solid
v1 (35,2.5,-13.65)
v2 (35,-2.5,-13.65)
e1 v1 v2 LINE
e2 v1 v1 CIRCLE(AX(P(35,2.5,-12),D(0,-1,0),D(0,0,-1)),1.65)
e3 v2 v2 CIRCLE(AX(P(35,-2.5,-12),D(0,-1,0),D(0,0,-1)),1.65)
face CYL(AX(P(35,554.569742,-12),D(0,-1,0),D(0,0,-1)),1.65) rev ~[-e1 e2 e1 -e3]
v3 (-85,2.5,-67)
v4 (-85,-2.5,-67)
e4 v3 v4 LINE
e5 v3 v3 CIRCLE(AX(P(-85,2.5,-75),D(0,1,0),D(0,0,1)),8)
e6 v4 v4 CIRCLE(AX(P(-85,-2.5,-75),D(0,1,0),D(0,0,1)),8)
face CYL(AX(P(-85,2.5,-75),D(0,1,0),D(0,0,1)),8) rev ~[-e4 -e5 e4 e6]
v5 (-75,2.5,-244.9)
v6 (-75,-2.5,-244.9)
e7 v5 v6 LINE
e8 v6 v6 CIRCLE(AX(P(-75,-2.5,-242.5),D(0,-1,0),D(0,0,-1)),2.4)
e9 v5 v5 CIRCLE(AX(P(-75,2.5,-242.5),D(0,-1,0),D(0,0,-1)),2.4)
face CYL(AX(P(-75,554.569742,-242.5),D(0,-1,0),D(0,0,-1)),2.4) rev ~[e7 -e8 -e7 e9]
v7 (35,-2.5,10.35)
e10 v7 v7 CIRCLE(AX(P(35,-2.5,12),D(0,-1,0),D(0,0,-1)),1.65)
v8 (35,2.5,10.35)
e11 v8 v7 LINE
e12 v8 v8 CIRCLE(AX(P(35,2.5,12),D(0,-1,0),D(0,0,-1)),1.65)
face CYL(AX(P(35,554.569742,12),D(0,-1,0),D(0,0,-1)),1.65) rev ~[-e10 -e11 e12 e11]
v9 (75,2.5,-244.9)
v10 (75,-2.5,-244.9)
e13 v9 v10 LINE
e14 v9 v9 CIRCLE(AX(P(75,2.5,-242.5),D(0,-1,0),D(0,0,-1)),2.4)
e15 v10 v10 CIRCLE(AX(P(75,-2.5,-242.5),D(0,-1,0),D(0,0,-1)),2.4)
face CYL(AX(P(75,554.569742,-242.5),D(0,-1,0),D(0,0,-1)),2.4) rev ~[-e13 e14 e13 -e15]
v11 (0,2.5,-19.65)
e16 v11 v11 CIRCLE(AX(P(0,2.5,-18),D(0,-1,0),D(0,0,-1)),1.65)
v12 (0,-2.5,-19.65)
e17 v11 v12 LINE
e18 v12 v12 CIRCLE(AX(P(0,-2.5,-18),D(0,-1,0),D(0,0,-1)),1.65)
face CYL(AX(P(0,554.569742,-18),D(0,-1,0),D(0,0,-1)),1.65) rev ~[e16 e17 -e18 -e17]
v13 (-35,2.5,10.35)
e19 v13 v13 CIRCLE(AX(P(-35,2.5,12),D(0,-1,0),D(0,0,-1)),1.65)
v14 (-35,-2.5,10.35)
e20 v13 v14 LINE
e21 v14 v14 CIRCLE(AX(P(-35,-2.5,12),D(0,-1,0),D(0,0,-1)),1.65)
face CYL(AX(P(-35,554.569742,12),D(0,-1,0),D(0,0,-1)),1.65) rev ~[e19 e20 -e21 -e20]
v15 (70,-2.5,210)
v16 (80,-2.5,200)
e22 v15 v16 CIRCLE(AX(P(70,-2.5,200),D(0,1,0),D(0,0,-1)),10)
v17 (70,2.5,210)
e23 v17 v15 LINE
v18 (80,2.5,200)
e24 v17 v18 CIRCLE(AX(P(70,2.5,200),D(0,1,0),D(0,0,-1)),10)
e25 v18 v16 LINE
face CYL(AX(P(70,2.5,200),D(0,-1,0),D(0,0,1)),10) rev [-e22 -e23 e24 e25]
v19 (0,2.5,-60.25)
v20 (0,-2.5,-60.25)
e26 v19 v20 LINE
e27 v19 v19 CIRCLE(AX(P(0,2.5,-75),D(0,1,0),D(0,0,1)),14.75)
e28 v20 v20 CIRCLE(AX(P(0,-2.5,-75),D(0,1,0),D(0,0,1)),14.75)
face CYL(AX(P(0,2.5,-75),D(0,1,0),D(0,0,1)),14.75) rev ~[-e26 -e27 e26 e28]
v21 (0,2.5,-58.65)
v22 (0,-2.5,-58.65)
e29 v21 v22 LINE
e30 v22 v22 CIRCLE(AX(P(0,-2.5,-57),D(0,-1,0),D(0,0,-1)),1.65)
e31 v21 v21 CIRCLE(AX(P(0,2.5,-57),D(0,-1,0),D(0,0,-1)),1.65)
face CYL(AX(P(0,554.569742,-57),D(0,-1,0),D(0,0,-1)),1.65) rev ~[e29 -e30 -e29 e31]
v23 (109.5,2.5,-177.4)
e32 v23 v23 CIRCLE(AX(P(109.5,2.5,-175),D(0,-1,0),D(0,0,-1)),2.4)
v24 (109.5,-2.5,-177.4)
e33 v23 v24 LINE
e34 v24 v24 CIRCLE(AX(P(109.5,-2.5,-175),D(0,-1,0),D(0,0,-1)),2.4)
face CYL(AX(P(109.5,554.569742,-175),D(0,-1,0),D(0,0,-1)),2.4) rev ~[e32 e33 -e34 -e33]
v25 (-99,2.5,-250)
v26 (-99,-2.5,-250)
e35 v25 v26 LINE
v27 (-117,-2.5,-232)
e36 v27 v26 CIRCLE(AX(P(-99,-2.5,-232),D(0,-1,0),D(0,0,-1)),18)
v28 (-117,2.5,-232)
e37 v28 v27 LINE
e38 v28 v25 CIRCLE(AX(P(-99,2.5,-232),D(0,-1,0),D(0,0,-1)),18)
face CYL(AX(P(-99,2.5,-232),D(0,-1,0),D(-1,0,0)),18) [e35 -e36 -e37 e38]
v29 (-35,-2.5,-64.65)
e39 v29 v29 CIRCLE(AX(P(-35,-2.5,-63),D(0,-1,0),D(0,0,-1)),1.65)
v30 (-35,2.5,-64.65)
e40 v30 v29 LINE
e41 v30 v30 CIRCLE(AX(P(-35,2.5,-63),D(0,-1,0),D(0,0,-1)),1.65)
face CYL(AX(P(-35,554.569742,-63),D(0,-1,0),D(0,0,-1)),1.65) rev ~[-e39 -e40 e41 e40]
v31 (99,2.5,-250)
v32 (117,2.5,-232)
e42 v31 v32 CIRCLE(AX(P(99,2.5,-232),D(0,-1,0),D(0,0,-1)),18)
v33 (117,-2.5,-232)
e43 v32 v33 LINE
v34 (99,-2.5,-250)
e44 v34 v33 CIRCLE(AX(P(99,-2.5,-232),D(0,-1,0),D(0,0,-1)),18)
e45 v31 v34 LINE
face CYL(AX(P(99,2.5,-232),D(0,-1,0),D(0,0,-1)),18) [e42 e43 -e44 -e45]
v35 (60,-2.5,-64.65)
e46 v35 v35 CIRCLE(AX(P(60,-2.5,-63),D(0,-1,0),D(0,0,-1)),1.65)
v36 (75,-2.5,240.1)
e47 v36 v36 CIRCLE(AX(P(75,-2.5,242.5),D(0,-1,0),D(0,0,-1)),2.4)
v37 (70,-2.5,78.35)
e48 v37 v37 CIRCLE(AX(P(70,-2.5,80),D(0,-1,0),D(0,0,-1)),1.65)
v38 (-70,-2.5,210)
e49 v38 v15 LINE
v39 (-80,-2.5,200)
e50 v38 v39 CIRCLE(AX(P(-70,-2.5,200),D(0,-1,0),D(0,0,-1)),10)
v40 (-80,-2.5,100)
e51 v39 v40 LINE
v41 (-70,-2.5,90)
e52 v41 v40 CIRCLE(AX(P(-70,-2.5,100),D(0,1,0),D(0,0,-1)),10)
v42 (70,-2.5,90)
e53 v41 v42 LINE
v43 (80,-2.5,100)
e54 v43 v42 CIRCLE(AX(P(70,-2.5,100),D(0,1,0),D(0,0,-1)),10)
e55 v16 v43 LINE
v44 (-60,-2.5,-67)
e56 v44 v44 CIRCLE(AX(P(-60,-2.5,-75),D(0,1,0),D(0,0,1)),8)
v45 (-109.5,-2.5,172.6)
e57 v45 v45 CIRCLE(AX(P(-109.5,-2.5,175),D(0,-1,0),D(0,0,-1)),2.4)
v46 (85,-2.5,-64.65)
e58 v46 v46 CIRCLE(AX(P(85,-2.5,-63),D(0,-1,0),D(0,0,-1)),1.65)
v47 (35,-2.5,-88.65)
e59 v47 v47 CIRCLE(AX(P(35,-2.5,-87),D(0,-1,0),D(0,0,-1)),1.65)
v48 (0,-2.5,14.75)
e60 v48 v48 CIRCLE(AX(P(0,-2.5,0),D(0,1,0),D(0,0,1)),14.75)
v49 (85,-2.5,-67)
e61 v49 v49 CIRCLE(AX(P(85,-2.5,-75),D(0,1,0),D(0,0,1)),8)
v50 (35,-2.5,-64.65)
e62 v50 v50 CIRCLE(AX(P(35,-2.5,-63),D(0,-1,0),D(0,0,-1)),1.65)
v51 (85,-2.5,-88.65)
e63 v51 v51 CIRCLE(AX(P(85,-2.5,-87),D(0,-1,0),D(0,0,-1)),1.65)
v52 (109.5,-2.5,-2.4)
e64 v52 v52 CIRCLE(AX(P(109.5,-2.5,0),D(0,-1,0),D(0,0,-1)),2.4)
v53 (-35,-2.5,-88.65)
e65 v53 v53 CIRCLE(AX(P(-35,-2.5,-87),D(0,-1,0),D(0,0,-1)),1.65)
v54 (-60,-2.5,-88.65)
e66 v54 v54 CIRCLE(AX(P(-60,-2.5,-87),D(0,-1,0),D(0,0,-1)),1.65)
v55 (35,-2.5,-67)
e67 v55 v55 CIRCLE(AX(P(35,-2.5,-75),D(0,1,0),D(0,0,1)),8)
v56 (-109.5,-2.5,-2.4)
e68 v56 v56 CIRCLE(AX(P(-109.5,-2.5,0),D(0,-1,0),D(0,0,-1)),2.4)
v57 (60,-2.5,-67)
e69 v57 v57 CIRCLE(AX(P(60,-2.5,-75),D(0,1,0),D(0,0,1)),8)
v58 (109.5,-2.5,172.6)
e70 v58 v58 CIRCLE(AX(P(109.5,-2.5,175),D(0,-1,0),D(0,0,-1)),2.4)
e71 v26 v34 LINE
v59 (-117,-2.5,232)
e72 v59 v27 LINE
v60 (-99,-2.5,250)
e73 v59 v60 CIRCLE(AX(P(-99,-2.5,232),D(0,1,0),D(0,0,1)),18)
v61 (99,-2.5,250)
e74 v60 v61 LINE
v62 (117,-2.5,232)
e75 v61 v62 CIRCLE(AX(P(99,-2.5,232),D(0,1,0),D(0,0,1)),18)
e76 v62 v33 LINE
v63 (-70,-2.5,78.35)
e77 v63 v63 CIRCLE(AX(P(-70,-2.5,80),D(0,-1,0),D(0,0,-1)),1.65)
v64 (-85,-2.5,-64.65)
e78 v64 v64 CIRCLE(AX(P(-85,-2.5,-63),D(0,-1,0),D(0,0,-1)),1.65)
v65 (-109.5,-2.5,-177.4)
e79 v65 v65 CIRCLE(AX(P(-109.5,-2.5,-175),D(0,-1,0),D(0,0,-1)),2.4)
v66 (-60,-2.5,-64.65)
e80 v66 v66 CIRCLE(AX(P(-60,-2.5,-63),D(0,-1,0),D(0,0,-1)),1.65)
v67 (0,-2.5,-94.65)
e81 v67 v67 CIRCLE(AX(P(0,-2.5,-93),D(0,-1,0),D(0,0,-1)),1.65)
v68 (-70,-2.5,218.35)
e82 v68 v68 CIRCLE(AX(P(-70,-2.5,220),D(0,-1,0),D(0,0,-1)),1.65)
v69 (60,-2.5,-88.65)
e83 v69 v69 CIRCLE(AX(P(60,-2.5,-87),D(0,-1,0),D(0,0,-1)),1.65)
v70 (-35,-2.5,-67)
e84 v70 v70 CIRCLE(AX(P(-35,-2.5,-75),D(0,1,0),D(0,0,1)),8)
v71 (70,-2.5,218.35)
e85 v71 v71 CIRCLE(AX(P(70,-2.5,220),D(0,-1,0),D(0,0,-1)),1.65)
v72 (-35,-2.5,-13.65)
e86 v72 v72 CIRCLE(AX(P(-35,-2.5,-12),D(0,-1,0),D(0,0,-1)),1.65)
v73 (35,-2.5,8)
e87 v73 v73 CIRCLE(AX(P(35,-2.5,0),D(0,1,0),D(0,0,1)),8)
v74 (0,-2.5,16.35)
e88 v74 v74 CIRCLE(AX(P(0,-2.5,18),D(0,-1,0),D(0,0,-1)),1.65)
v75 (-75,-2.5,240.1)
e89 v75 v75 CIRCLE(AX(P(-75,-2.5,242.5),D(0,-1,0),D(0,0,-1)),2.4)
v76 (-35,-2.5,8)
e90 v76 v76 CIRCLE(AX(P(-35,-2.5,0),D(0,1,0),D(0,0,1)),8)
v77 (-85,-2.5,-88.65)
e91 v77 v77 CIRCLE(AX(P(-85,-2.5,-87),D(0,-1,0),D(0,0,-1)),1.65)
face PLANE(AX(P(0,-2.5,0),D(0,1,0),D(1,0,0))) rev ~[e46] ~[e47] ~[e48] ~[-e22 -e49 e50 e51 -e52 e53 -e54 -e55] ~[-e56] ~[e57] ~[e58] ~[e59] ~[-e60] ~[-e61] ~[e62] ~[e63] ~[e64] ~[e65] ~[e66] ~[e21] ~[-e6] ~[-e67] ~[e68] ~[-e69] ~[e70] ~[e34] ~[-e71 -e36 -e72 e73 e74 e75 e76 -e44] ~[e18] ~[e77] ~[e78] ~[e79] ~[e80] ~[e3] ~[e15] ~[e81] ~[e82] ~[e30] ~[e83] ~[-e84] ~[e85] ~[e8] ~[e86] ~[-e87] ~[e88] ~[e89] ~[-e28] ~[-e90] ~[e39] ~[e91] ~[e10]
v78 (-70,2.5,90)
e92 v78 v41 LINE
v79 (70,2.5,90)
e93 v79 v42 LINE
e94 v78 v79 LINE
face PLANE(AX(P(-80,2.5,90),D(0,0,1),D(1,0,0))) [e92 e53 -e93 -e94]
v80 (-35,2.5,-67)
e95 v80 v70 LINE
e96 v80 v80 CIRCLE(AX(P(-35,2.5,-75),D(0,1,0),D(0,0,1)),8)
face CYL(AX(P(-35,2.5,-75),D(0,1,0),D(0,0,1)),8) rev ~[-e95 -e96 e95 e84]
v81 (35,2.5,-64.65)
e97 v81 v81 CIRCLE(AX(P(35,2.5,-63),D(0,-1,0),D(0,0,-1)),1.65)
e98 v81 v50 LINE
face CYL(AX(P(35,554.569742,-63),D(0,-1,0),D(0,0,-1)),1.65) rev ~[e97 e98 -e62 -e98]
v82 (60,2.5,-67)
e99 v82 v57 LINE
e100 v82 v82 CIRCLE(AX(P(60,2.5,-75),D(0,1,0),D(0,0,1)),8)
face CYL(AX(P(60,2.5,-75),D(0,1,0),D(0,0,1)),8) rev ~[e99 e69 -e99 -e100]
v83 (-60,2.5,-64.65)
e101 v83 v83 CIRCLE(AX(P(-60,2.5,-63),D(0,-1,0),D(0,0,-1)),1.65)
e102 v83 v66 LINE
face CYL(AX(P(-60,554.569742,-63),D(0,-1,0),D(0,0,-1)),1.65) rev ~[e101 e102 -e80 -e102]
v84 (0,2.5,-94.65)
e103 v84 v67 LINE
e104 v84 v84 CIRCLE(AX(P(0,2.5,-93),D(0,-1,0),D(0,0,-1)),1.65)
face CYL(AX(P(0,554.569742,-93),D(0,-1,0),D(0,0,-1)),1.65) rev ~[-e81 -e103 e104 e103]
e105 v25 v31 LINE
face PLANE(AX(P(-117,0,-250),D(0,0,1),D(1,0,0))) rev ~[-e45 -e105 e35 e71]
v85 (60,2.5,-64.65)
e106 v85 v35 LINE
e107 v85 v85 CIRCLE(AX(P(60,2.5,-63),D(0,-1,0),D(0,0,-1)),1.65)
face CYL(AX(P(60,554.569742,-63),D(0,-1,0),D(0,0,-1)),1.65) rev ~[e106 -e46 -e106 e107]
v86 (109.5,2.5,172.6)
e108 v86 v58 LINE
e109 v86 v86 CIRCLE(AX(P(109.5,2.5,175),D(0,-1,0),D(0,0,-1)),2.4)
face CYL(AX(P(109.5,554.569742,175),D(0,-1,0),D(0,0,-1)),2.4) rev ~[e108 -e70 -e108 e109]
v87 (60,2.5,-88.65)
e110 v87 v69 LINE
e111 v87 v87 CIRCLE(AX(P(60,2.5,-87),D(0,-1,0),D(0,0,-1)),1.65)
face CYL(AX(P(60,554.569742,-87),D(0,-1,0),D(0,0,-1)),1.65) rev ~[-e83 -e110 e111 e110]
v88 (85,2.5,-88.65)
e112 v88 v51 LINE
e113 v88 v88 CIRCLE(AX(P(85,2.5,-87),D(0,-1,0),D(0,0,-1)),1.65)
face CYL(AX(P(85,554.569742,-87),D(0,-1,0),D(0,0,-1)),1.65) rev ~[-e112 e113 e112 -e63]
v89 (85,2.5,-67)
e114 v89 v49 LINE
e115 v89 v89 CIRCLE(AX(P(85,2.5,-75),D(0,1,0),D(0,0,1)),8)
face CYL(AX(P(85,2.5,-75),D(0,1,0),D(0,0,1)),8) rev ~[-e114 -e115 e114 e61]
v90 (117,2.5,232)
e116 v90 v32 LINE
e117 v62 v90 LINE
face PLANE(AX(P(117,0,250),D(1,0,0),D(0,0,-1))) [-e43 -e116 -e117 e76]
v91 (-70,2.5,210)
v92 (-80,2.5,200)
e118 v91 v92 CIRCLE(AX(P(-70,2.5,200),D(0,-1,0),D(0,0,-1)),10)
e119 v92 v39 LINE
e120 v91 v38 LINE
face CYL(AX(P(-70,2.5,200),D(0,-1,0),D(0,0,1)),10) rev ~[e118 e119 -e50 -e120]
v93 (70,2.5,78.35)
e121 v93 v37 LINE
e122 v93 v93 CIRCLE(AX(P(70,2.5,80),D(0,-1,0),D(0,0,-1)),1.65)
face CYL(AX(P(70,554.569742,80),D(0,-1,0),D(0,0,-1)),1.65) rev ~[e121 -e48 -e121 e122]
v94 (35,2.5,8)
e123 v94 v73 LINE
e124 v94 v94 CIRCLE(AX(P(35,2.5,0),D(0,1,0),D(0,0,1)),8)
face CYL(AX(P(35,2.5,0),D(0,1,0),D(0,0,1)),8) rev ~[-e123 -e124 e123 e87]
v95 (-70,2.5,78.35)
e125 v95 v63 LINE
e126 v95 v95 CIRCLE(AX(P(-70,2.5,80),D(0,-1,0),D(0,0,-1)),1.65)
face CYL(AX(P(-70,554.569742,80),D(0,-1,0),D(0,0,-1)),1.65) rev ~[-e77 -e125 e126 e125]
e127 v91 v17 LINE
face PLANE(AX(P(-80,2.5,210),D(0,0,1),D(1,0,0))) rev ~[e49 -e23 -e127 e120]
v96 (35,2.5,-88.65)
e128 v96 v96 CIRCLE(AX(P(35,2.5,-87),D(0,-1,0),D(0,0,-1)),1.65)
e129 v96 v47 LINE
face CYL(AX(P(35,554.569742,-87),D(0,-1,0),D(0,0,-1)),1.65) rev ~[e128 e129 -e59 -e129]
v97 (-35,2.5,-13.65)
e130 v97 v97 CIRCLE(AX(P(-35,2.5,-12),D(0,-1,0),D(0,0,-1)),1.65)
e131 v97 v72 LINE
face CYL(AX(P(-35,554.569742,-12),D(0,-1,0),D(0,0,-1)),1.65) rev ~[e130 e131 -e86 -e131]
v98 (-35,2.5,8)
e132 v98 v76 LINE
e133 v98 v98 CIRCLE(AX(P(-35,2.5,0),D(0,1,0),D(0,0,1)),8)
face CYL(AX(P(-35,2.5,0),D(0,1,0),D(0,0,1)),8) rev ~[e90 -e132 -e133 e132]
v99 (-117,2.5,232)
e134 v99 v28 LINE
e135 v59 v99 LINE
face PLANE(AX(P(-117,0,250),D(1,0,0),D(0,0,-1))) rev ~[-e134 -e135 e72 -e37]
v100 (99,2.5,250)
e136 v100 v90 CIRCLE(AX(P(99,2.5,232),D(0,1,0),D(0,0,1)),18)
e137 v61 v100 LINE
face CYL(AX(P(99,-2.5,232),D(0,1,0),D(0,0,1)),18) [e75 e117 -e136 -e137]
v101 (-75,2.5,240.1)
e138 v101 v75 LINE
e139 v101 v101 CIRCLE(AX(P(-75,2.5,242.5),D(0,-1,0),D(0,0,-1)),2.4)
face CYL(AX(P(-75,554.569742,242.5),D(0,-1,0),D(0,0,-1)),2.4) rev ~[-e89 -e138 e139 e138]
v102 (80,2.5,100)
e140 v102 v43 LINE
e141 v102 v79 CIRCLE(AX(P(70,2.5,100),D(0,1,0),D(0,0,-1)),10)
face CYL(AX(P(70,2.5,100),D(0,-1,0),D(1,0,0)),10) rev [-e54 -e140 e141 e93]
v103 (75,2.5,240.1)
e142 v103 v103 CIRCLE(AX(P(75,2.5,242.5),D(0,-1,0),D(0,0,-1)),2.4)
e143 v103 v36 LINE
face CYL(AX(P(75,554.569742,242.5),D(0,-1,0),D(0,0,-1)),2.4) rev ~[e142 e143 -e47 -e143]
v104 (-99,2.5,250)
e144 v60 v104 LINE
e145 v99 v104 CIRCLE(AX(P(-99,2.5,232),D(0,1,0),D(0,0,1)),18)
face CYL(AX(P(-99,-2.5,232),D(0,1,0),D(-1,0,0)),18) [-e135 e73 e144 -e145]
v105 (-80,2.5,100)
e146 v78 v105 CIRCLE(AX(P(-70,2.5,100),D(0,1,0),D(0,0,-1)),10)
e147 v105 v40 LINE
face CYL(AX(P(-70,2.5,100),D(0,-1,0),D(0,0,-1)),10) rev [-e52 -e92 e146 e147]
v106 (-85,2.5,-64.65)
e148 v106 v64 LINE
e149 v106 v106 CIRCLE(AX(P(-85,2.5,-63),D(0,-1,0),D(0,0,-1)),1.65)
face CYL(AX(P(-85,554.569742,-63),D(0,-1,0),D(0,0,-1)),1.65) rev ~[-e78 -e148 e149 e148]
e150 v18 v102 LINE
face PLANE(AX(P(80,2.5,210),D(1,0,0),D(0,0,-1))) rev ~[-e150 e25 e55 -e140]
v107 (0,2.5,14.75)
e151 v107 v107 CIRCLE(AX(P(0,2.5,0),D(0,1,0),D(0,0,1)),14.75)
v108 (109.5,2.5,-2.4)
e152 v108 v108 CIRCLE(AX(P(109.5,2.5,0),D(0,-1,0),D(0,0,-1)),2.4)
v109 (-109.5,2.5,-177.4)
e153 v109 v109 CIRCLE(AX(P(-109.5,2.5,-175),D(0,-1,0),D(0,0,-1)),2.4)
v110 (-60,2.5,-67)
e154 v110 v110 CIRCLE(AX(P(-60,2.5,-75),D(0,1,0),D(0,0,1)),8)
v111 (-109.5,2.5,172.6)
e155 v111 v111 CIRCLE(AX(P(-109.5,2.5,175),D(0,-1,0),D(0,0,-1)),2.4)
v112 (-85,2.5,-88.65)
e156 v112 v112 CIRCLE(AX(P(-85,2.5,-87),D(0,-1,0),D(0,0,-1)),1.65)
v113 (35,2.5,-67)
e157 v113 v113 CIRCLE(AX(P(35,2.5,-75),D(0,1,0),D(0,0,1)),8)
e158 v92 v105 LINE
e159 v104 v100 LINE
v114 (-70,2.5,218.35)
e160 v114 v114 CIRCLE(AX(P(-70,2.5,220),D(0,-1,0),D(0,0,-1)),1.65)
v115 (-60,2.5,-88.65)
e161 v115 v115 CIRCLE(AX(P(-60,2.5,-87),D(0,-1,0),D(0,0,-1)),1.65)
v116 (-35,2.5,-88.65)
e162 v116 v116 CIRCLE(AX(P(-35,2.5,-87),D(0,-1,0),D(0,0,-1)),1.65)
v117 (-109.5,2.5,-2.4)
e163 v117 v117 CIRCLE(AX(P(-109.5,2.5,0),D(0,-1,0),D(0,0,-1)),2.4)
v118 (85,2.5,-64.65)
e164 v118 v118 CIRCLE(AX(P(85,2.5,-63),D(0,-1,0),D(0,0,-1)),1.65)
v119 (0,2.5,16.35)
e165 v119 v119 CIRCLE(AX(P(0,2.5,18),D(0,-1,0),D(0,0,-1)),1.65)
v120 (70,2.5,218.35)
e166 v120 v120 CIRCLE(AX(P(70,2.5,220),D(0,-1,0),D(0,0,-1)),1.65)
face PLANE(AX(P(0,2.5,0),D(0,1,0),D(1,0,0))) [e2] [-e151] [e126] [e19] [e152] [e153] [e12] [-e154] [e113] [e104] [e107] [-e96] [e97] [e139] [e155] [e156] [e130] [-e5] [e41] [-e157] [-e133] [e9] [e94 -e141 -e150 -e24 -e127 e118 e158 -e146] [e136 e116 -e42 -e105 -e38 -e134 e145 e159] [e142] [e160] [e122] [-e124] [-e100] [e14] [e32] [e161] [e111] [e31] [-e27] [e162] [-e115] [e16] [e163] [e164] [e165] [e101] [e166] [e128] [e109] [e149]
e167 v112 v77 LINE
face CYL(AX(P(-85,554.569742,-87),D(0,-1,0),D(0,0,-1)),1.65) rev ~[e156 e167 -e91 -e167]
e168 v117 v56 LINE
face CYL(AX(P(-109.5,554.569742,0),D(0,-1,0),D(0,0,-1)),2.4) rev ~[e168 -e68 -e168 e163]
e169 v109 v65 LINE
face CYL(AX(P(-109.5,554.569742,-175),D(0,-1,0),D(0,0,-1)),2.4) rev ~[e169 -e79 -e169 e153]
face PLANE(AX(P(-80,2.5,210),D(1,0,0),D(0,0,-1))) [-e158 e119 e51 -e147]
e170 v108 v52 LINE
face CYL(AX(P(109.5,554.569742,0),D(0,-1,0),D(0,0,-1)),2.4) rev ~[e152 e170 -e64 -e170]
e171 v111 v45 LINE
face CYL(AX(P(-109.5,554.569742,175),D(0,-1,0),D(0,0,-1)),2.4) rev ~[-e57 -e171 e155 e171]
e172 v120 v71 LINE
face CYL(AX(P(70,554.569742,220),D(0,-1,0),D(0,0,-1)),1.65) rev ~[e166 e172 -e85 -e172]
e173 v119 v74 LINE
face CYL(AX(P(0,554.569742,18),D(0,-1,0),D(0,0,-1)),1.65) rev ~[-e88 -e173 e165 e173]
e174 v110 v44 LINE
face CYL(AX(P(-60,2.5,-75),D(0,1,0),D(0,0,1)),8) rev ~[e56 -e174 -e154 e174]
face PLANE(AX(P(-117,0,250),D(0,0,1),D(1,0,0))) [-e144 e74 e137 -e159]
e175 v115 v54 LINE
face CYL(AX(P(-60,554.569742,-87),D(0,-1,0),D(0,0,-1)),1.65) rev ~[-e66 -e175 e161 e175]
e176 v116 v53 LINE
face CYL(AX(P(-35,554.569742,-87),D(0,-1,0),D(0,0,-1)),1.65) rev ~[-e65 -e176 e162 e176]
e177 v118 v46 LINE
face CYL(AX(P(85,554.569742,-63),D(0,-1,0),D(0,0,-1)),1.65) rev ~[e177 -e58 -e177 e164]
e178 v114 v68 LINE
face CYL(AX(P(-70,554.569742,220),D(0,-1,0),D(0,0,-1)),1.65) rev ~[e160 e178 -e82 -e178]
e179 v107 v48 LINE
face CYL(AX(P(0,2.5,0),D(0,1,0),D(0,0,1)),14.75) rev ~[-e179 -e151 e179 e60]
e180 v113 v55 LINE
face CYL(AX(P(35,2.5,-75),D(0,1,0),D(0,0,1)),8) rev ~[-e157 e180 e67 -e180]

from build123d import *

# Parameters (mm, degrees)
SKETCH1_W            = 234
SKETCH1_H            = 500
BOSS_EXTRUDE1_DEPTH  = 2.5
M4_CLEARANCE_HOLE1_D = 4.8
FILLET1_R            = 18
M4_TAPPED_HOLE7_D    = 3.3
SKETCH4_R            = 14.75
SKETCH4_R_2          = 8
CUT_EXTRUDE6_DEPTH   = 277.068831997
M4_TAPPED_HOLE3_D    = 3.3
SKETCH9_R            = 14.75
CUT_EXTRUDE3_DEPTH   = 277.068831997
M4_TAPPED_HOLE4_D    = 3.3
SKETCH12_W           = 160
SKETCH12_H           = 120
CUT_EXTRUDE4_DEPTH   = 277.068831997
FILLET2_R            = 10


with BuildPart() as part:
    # Sketch1 → Boss-Extrude1 (new, symmetric)
    with BuildSketch(Plane(origin=(0, 0, 0), x_dir=(1, 0, 0), z_dir=(0, 1, 0))):
        Rectangle(SKETCH1_W, SKETCH1_H)
    extrude(amount=BOSS_EXTRUDE1_DEPTH, both=True)

    # M4 Clearance Hole1 (through all)
    with Locations(Plane(origin=(-75, 2.5, -242.5), x_dir=(0, 0, 1), z_dir=(0, 1, 0))):
        with Locations((0, 0), (0, 150), (67.5, 184.5), (67.5, -34.5), (242.5, 184.5), (242.5, -34.5), (417.5, -34.5), (417.5, 184.5), (485, 0), (485, 150)):
            Hole(M4_CLEARANCE_HOLE1_D / 2)

    # Fillet1
    fillet1_edges = [part.edges().sort_by_distance(p)[0] for p in [
        (117, 0, 250),
        (-117, 0, 250),
        (-117, 0, -250),
        (117, 0, -250),
    ]]
    fillet(fillet1_edges, radius=FILLET1_R)

    # M4 Tapped Hole7 (through all)
    with Locations(Plane(origin=(-85, 2.5, -87), x_dir=(0, 0, 1), z_dir=(0, 1, 0))):
        with Locations((0, 0), (24, 0), (24, 25), (0, 25), (0, 50), (24, 50), (-6, 85), (30, 85), (0, 120), (24, 120), (0, 145), (24, 145), (0, 170), (24, 170), (75, 120), (99, 120), (75, 50), (99, 50)):
            Hole(M4_TAPPED_HOLE7_D / 2)

    # Sketch4 → Cut-Extrude6 (cut, through all)
    with BuildSketch(Plane(origin=(0, 2.5, 0), x_dir=(1, 0, 0), z_dir=(0, 1, 0))):
        with Locations(Location((0, 75, 0), (0, 0, 270))):
            Circle(SKETCH4_R)
        with Locations(Location((-35, 75, 0), (0, 0, 270))):
            Circle(SKETCH4_R_2)
        with Locations(Location((35, 75, 0), (0, 0, 270))):
            Circle(SKETCH4_R_2)
        with Locations(Location((-60, 75, 0), (0, 0, 270))):
            Circle(SKETCH4_R_2)
        with Locations(Location((-85, 75, 0), (0, 0, 270))):
            Circle(SKETCH4_R_2)
        with Locations(Location((60, 75, 0), (0, 0, 270))):
            Circle(SKETCH4_R_2)
        with Locations(Location((85, 75, 0), (0, 0, 270))):
            Circle(SKETCH4_R_2)
        with Locations(Location((35, 0, 0), (0, 0, 270))):
            Circle(SKETCH4_R_2)
        with Locations(Location((-35, 0, 0), (0, 0, 270))):
            Circle(SKETCH4_R_2)
    extrude(amount=-CUT_EXTRUDE6_DEPTH, mode=Mode.SUBTRACT)

    # M4 Tapped Hole3 (through all)
    with Locations(Plane(origin=(0, 2.5, -18), x_dir=(0, 0, 1), z_dir=(0, 1, 0))):
        with Locations((0, 0), (36, 0)):
            Hole(M4_TAPPED_HOLE3_D / 2)

    # Sketch9 → Cut-Extrude3 (cut, through all)
    with BuildSketch(Plane(origin=(0, 2.5, 0), x_dir=(1, 0, 0), z_dir=(0, 1, 0))):
        with Locations(Location((0, 0, 0), (0, 0, 270))):
            Circle(SKETCH9_R)
    extrude(amount=-CUT_EXTRUDE3_DEPTH, mode=Mode.SUBTRACT)

    # M4 Tapped Hole4 (through all)
    with Locations(Plane(origin=(-70, 2.5, 80), x_dir=(0, 0, 1), z_dir=(0, 1, 0))):
        with Locations((0, 0), (0, 140), (140, 140), (140, 0)):
            Hole(M4_TAPPED_HOLE4_D / 2)

    # Sketch12 → Cut-Extrude4 (cut, through all)
    with BuildSketch(Plane(origin=(0, 2.5, 0), x_dir=(1, 0, 0), z_dir=(0, 1, 0))):
        with Locations((0, -150)):
            Rectangle(SKETCH12_W, SKETCH12_H)
    extrude(amount=-CUT_EXTRUDE4_DEPTH, mode=Mode.SUBTRACT)

    # Fillet2
    fillet2_edges = [part.edges().sort_by_distance(p)[0] for p in [
        (80, 0, 90),
        (80, 0, 210),
        (-80, 0, 210),
        (-80, 0, 90),
    ]]
    fillet(fillet2_edges, radius=FILLET2_R)


solid = part.part
